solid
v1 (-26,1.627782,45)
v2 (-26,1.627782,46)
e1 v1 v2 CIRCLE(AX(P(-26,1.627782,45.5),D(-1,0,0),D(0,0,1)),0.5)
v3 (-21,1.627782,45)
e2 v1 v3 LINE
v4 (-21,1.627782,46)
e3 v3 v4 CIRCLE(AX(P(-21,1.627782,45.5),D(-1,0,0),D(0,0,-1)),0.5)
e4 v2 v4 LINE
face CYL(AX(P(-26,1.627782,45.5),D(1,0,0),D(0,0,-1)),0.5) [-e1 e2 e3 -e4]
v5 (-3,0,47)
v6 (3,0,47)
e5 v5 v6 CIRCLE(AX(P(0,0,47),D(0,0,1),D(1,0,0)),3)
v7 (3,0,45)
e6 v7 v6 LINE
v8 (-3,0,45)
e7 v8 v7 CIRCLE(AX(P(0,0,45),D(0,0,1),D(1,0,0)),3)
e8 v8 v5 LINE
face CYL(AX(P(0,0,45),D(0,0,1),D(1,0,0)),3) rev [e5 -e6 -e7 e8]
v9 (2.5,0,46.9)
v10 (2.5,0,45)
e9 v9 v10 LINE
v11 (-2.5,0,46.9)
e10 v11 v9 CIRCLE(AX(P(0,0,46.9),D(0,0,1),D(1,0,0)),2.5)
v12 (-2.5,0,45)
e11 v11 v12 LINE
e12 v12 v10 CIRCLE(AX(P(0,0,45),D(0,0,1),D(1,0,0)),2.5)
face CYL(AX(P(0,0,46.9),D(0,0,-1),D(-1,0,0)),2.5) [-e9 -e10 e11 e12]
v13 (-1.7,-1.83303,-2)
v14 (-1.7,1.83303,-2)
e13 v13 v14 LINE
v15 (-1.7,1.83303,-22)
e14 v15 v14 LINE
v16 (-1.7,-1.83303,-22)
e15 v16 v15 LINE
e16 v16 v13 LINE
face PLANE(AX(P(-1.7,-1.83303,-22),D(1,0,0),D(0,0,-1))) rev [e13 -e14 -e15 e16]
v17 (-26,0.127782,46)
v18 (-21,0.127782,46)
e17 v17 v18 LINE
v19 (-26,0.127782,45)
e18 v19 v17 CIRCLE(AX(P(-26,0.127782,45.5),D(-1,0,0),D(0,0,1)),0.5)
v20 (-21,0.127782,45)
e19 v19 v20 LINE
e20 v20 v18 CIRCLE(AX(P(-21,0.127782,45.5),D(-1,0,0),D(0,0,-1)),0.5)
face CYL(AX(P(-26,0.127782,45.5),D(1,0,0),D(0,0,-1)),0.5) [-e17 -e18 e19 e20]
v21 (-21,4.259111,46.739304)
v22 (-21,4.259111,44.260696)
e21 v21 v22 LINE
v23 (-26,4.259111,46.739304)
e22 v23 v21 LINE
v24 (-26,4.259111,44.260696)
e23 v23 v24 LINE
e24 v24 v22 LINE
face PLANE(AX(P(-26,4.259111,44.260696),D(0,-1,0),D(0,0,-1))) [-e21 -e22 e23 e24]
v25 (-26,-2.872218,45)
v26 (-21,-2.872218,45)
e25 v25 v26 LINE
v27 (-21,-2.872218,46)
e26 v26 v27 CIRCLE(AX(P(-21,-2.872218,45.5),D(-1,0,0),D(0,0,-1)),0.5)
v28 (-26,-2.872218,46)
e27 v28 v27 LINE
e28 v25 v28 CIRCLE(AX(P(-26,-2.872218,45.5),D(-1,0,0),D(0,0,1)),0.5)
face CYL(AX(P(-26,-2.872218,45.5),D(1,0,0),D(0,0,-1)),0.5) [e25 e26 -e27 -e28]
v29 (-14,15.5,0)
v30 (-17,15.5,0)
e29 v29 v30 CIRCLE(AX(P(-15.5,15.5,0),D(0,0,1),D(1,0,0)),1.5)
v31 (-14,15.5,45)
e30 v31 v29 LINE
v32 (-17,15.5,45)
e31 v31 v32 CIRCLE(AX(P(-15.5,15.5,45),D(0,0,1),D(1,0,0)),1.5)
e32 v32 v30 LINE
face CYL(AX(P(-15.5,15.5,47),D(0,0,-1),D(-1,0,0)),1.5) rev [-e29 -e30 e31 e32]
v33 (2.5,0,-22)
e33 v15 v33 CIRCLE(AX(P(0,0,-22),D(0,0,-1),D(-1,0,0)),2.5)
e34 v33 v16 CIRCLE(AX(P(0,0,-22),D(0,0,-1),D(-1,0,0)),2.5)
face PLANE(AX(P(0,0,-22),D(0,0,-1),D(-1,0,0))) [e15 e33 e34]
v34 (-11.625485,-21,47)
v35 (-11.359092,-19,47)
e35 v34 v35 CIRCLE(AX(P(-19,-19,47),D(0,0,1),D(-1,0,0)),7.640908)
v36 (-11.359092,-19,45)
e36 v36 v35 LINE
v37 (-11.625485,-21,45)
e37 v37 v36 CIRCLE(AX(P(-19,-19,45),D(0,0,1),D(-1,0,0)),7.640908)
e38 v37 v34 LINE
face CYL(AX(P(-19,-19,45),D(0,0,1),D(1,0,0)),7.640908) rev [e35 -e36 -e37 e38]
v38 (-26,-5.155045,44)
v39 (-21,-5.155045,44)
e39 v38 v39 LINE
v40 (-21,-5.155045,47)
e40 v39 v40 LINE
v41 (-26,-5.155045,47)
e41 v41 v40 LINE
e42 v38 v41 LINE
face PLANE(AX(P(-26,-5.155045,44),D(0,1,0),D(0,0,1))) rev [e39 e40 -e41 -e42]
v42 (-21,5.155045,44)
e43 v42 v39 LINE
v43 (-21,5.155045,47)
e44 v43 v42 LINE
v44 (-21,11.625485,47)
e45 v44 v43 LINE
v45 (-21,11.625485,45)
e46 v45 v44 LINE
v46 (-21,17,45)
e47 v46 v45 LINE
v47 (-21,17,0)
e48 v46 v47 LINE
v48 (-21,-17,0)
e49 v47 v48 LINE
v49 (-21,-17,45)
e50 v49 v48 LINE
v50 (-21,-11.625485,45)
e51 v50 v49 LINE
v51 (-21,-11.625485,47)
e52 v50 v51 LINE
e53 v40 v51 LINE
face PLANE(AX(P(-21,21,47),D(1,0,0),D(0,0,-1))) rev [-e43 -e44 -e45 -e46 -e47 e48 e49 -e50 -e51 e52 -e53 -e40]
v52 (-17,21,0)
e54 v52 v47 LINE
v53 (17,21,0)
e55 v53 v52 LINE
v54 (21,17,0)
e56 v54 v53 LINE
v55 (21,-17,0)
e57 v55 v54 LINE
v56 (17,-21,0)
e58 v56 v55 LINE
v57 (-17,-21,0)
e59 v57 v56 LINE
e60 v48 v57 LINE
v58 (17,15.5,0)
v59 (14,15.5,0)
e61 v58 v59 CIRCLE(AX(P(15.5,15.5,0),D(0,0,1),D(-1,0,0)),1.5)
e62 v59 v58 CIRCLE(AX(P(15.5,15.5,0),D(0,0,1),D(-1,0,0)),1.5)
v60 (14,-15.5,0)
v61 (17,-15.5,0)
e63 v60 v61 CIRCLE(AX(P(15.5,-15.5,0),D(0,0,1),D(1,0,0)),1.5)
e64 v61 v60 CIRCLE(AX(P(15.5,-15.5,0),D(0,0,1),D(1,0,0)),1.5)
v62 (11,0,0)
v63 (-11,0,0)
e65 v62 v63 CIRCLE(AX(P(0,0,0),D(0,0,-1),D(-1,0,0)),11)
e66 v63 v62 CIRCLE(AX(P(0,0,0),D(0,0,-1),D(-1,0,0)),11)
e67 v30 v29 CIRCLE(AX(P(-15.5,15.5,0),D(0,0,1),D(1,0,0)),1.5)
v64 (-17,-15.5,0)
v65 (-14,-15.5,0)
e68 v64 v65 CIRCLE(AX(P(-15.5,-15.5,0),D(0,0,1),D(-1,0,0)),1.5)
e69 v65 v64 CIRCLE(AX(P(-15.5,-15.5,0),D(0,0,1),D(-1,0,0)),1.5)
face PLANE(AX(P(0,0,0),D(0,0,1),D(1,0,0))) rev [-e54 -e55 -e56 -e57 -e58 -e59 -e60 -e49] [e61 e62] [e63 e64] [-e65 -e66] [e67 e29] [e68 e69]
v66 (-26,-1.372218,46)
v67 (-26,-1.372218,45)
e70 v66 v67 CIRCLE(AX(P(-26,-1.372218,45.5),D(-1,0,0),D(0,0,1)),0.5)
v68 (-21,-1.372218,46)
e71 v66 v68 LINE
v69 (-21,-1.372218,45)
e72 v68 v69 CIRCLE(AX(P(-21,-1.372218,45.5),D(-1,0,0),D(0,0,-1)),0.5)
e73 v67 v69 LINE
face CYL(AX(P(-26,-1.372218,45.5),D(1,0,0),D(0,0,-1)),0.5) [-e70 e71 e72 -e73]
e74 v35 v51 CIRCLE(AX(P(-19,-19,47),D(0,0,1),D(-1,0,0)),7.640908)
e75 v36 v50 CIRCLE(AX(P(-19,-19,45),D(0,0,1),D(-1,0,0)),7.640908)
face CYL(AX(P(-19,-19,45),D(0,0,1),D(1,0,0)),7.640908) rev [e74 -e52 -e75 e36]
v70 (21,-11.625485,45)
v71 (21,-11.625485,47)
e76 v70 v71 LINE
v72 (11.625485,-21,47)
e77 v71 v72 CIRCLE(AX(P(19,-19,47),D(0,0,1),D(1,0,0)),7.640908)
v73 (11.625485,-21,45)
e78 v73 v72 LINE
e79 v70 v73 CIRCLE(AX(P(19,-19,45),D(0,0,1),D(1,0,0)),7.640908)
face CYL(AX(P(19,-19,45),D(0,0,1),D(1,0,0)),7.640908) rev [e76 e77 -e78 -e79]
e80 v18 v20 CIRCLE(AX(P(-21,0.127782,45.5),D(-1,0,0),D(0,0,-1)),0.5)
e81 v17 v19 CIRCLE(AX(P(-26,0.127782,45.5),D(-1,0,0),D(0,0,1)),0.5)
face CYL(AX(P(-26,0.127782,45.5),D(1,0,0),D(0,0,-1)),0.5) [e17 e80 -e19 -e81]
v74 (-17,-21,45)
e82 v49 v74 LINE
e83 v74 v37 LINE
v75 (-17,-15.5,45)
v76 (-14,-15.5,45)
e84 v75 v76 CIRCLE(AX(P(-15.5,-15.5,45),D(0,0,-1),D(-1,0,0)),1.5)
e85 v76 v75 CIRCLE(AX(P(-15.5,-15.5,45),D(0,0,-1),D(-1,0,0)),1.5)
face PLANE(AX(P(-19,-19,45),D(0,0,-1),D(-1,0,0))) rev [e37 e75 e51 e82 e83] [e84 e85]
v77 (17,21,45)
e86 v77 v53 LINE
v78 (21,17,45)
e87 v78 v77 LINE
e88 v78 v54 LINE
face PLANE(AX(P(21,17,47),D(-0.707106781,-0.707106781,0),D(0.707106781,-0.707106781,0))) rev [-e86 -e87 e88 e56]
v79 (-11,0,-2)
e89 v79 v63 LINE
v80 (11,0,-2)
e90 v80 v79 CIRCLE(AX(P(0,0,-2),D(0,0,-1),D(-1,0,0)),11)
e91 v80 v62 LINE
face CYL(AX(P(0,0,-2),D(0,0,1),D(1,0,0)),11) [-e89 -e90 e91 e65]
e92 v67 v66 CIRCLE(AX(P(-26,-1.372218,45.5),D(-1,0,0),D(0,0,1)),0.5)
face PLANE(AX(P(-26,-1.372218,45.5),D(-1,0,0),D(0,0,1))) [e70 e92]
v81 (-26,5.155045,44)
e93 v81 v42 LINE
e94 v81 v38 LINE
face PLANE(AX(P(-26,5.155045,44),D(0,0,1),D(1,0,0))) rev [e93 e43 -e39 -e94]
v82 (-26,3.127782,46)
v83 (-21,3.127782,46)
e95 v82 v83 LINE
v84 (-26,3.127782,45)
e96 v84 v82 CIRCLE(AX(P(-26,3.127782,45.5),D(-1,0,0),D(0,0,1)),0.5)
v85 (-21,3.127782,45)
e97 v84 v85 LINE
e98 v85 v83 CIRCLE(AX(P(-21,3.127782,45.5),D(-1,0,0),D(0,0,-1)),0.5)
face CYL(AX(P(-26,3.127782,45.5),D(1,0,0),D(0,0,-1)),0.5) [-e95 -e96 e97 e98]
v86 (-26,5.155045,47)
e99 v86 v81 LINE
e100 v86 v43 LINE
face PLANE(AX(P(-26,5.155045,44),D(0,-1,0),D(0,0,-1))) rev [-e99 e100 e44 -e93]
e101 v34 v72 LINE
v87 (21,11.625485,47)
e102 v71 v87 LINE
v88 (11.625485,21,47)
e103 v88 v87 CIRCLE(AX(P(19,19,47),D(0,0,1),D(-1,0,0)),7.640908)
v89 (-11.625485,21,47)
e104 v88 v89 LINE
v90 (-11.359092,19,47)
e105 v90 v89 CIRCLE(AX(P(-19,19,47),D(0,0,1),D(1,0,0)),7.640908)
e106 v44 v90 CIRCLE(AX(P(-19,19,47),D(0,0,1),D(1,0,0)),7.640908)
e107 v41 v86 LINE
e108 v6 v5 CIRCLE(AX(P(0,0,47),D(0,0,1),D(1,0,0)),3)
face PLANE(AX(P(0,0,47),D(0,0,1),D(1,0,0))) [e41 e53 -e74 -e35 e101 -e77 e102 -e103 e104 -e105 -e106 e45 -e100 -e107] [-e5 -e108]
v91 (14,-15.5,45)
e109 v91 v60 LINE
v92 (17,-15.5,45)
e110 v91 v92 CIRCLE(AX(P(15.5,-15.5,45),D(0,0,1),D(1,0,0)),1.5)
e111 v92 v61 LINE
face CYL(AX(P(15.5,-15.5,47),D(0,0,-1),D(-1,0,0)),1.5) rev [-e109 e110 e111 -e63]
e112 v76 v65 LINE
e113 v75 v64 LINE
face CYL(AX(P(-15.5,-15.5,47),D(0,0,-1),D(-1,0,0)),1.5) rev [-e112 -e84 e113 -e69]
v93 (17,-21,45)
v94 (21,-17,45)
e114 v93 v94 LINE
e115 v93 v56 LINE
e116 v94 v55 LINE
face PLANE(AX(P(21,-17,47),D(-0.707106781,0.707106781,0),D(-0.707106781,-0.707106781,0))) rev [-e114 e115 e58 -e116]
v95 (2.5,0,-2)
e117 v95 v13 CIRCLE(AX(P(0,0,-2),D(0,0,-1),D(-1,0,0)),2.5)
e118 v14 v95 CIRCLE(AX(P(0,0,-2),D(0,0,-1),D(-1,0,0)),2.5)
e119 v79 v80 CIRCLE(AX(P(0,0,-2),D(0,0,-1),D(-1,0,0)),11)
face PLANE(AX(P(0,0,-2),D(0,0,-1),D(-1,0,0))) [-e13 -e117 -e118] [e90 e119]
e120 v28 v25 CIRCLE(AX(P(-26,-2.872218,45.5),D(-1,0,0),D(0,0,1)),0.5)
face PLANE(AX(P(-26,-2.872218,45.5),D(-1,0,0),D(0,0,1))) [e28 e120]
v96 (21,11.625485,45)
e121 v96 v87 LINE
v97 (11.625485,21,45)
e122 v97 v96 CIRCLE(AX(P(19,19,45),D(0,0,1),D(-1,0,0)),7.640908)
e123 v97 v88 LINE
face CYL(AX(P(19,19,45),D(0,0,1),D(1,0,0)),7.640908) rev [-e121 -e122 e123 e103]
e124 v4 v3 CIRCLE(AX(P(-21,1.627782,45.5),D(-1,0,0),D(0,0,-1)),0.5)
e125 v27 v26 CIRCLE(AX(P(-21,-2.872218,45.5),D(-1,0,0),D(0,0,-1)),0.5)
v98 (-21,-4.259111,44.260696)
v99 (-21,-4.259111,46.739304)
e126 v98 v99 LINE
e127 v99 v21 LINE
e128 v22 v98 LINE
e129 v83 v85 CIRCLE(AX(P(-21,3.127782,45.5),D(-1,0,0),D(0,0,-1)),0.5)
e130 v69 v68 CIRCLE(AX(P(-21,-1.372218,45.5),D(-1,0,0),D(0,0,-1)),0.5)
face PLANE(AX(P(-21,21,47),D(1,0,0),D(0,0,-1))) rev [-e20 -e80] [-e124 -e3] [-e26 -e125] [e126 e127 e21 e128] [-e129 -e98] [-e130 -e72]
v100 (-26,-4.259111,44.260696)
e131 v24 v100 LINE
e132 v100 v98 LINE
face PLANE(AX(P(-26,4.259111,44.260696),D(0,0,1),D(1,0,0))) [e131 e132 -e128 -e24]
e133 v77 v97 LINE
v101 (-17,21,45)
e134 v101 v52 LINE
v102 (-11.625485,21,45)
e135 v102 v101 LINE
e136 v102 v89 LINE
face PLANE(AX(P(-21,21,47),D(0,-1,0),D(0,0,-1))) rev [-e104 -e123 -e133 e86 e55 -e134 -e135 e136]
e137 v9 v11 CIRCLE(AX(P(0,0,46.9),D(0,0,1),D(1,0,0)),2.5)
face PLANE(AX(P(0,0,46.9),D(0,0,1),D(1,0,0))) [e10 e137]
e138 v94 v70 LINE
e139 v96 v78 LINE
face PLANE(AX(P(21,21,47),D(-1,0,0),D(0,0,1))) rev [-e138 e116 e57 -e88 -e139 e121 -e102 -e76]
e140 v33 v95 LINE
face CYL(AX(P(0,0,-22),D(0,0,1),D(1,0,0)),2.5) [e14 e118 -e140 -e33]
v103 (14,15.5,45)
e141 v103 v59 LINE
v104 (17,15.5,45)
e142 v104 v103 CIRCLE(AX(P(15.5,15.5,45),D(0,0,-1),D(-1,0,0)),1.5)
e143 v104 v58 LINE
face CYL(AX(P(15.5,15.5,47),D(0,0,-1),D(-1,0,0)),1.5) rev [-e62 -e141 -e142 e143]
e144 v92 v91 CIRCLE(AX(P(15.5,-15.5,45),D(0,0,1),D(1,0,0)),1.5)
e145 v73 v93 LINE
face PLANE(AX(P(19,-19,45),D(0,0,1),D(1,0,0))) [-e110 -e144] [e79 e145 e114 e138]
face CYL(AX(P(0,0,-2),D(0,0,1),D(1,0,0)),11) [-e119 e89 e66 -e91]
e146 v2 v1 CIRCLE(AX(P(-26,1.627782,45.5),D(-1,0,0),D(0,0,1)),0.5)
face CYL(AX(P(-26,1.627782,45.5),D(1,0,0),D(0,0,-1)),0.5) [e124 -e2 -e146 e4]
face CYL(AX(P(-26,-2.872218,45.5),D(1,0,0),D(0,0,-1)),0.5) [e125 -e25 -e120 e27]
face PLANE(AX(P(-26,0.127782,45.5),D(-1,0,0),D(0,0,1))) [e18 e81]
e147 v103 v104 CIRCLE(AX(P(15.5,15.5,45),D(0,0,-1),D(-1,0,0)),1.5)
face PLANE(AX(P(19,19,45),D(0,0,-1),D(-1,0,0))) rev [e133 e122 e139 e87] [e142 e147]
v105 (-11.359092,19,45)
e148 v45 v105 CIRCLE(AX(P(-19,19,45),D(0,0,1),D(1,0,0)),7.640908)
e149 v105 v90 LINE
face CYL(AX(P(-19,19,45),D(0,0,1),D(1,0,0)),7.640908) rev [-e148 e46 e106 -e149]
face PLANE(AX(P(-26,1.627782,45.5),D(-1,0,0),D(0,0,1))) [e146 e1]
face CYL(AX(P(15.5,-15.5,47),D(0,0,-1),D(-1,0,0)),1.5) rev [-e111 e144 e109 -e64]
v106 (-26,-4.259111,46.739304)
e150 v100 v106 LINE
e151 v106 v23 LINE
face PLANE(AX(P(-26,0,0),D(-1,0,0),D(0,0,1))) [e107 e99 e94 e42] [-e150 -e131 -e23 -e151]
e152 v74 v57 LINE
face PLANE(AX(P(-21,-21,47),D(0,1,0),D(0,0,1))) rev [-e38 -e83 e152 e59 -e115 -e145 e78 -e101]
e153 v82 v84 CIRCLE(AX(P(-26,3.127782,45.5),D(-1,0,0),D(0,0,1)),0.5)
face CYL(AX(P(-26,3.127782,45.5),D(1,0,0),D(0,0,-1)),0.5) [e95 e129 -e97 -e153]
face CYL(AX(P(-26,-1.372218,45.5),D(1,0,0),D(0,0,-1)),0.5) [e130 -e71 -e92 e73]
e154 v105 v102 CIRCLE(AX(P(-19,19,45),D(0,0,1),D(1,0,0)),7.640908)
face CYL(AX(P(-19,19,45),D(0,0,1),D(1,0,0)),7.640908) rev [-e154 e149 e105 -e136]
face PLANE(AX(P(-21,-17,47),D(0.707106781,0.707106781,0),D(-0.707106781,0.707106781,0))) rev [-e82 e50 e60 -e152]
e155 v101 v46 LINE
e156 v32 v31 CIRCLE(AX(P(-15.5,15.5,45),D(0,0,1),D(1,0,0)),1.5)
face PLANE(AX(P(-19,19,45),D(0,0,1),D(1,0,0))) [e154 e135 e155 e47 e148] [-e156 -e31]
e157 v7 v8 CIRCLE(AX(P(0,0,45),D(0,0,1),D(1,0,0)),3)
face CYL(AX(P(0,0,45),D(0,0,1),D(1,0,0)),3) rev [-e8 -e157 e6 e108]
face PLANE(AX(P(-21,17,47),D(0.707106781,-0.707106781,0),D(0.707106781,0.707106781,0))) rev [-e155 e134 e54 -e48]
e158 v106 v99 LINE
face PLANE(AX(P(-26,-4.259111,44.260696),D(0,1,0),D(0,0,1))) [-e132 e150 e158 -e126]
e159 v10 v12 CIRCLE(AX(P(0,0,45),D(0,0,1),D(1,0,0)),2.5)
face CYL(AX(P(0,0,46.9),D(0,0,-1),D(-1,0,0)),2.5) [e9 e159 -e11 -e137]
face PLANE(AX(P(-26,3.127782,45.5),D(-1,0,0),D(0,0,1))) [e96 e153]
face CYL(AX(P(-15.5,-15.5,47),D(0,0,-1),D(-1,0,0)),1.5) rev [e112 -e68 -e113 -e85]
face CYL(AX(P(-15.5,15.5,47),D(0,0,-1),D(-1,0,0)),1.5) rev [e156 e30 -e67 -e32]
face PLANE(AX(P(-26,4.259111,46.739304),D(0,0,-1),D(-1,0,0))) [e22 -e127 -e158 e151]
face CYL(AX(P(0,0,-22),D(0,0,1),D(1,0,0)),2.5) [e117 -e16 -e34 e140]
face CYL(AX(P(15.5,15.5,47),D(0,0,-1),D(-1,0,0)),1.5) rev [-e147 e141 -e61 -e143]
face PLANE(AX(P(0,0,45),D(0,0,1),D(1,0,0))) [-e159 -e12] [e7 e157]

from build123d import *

# Parameters (mm, degrees)
SKETCH1_W           = 42
SKETCH1_H           = 42
SKETCH1_R           = 1.5
BOSS_EXTRUDE1_DEPTH = 47
CUT_EXTRUDE1_DEPTH  = 56.596762496
SKETCH4_R           = 11
BOSS_EXTRUDE2_DEPTH = 2
BOSS_EXTRUDE3_DEPTH = 20
CUT_EXTRUDE2_DEPTH  = 2
SKETCH8_R           = 3
CUT_EXTRUDE3_DEPTH  = 2
BOSS_EXTRUDE4_START = 1.9
SKETCH9_R           = 2.5
BOSS_EXTRUDE4_DEPTH = 1.9
SKETCH10_W          = 3
SKETCH10_H          = 10.31009041
SKETCH10_W_2        = 2.478607588
SKETCH10_H_2        = 8.518222776
BOSS_EXTRUDE5_DEPTH = 5
SKETCH11_R          = 0.5
BOSS_EXTRUDE6_DEPTH = 5


with BuildPart() as part:
    # Sketch1 → Boss-Extrude1 (new body)
    with BuildSketch(Plane.XY):
        Rectangle(SKETCH1_W, SKETCH1_H)
        with Locations((-15.5, 15.5)):
            Circle(SKETCH1_R, mode=Mode.SUBTRACT)
        with Locations(Location((15.5, 15.5, 0), (0, 0, 180))):
            Circle(SKETCH1_R, mode=Mode.SUBTRACT)
        with Locations(Location((-15.5, -15.5, 0), (0, 0, 180))):
            Circle(SKETCH1_R, mode=Mode.SUBTRACT)
        with Locations((15.5, -15.5)):
            Circle(SKETCH1_R, mode=Mode.SUBTRACT)
    extrude(amount=BOSS_EXTRUDE1_DEPTH)

    # Sketch3 → Cut-Extrude1 (cut, through all)
    with BuildSketch(Plane(origin=(0, 0, 0), x_dir=(-1, 0, 0), z_dir=(0, 0, -1))):
        Polygon((-21, 17), (-17, 21), (-21, 21), align=None)
        Polygon((21, 21), (17, 21), (21, 17), align=None)
        Polygon((21, -17), (17, -21), (21, -21), align=None)
        Polygon((-21, -21), (-17, -21), (-21, -17), align=None)
    extrude(amount=-CUT_EXTRUDE1_DEPTH, mode=Mode.SUBTRACT)

    # Sketch4 → Boss-Extrude2 (add)
    with BuildSketch(Plane(origin=(0, 0, 0), x_dir=(-1, 0, 0), z_dir=(0, 0, -1))):
        Circle(SKETCH4_R)
    extrude(amount=BOSS_EXTRUDE2_DEPTH)

    # Sketch5 → Boss-Extrude3 (add)
    with BuildSketch(Plane(origin=(0, 0, -2), x_dir=(-1, 0, 0), z_dir=(0, 0, -1))):
        with BuildLine():
            Line((1.7, -1.833030278), (1.7, 1.833030278))
            ThreePointArc((1.7, 1.833030278), (-2.5, 0), (1.7, -1.833030278))
        make_face()
    extrude(amount=BOSS_EXTRUDE3_DEPTH)

    # Sketch7 → Cut-Extrude2 (cut)
    with BuildSketch(Plane.XY.offset(47)):
        with BuildLine():
            Line((21, 17), (21, 11.625484678))
            ThreePointArc((21, 11.625484678), (13.597062084, 13.597062084), (11.625484678, 21))
            Line((11.625484678, 21), (17, 21))
            Line((17, 21), (21, 17))
        make_face()
        with BuildLine():
            Line((-21, -17), (-21, -11.625484678))
            ThreePointArc((-21, -11.625484678), (-13.597062084, -13.597062084), (-11.625484678, -21))
            Line((-11.625484678, -21), (-17, -21))
            Line((-17, -21), (-21, -17))
        make_face()
        with BuildLine():
            Line((-11.625484678, 21), (-17, 21))
            Line((-17, 21), (-21, 17))
            Line((-21, 17), (-21, 11.625484678))
            ThreePointArc((-21, 11.625484678), (-13.597062084, 13.597062084), (-11.625484678, 21))
        make_face()
        with BuildLine():
            Line((11.625484678, -21), (17, -21))
            Line((17, -21), (21, -17))
            Line((21, -17), (21, -11.625484678))
            ThreePointArc((21, -11.625484678), (13.597062084, -13.597062084), (11.625484678, -21))
        make_face()
    extrude(amount=-CUT_EXTRUDE2_DEPTH, mode=Mode.SUBTRACT)

    # Sketch8 → Cut-Extrude3 (cut)
    with BuildSketch(Plane.XY.offset(47)):
        Circle(SKETCH8_R)
    extrude(amount=-CUT_EXTRUDE3_DEPTH, mode=Mode.SUBTRACT)

    # Sketch9 → Boss-Extrude4 (add)
    with BuildSketch(Plane.XY.offset(45).offset(BOSS_EXTRUDE4_START)):
        with Locations(Location((0, 0, 0), (0, 0, 180))):
            Circle(SKETCH9_R)
    extrude(amount=-BOSS_EXTRUDE4_DEPTH)

    # Sketch10 → Boss-Extrude5 (add)
    with BuildSketch(Plane.ZY.offset(21)):
        with Locations((45.5, 0)):
            Rectangle(SKETCH10_W, SKETCH10_H)
        with Locations((45.5, 0)):
            Rectangle(SKETCH10_W_2, SKETCH10_H_2, mode=Mode.SUBTRACT)
    extrude(amount=BOSS_EXTRUDE5_DEPTH)

    # Sketch11 → Boss-Extrude6 (add)
    with BuildSketch(Plane.ZY.offset(21)):
        with Locations(Location((45.5, 3.127782029, 0), (0, 0, 180))):
            Circle(SKETCH11_R)
        with Locations(Location((45.5, 1.627782029, 0), (0, 0, 180))):
            Circle(SKETCH11_R)
        with Locations(Location((45.5, 0.127782029, 0), (0, 0, 180))):
            Circle(SKETCH11_R)
        with Locations(Location((45.5, -1.372217971, 0), (0, 0, 180))):
            Circle(SKETCH11_R)
        with Locations(Location((45.5, -2.872217971, 0), (0, 0, 180))):
            Circle(SKETCH11_R)
    extrude(amount=BOSS_EXTRUDE6_DEPTH)


solid = part.part
